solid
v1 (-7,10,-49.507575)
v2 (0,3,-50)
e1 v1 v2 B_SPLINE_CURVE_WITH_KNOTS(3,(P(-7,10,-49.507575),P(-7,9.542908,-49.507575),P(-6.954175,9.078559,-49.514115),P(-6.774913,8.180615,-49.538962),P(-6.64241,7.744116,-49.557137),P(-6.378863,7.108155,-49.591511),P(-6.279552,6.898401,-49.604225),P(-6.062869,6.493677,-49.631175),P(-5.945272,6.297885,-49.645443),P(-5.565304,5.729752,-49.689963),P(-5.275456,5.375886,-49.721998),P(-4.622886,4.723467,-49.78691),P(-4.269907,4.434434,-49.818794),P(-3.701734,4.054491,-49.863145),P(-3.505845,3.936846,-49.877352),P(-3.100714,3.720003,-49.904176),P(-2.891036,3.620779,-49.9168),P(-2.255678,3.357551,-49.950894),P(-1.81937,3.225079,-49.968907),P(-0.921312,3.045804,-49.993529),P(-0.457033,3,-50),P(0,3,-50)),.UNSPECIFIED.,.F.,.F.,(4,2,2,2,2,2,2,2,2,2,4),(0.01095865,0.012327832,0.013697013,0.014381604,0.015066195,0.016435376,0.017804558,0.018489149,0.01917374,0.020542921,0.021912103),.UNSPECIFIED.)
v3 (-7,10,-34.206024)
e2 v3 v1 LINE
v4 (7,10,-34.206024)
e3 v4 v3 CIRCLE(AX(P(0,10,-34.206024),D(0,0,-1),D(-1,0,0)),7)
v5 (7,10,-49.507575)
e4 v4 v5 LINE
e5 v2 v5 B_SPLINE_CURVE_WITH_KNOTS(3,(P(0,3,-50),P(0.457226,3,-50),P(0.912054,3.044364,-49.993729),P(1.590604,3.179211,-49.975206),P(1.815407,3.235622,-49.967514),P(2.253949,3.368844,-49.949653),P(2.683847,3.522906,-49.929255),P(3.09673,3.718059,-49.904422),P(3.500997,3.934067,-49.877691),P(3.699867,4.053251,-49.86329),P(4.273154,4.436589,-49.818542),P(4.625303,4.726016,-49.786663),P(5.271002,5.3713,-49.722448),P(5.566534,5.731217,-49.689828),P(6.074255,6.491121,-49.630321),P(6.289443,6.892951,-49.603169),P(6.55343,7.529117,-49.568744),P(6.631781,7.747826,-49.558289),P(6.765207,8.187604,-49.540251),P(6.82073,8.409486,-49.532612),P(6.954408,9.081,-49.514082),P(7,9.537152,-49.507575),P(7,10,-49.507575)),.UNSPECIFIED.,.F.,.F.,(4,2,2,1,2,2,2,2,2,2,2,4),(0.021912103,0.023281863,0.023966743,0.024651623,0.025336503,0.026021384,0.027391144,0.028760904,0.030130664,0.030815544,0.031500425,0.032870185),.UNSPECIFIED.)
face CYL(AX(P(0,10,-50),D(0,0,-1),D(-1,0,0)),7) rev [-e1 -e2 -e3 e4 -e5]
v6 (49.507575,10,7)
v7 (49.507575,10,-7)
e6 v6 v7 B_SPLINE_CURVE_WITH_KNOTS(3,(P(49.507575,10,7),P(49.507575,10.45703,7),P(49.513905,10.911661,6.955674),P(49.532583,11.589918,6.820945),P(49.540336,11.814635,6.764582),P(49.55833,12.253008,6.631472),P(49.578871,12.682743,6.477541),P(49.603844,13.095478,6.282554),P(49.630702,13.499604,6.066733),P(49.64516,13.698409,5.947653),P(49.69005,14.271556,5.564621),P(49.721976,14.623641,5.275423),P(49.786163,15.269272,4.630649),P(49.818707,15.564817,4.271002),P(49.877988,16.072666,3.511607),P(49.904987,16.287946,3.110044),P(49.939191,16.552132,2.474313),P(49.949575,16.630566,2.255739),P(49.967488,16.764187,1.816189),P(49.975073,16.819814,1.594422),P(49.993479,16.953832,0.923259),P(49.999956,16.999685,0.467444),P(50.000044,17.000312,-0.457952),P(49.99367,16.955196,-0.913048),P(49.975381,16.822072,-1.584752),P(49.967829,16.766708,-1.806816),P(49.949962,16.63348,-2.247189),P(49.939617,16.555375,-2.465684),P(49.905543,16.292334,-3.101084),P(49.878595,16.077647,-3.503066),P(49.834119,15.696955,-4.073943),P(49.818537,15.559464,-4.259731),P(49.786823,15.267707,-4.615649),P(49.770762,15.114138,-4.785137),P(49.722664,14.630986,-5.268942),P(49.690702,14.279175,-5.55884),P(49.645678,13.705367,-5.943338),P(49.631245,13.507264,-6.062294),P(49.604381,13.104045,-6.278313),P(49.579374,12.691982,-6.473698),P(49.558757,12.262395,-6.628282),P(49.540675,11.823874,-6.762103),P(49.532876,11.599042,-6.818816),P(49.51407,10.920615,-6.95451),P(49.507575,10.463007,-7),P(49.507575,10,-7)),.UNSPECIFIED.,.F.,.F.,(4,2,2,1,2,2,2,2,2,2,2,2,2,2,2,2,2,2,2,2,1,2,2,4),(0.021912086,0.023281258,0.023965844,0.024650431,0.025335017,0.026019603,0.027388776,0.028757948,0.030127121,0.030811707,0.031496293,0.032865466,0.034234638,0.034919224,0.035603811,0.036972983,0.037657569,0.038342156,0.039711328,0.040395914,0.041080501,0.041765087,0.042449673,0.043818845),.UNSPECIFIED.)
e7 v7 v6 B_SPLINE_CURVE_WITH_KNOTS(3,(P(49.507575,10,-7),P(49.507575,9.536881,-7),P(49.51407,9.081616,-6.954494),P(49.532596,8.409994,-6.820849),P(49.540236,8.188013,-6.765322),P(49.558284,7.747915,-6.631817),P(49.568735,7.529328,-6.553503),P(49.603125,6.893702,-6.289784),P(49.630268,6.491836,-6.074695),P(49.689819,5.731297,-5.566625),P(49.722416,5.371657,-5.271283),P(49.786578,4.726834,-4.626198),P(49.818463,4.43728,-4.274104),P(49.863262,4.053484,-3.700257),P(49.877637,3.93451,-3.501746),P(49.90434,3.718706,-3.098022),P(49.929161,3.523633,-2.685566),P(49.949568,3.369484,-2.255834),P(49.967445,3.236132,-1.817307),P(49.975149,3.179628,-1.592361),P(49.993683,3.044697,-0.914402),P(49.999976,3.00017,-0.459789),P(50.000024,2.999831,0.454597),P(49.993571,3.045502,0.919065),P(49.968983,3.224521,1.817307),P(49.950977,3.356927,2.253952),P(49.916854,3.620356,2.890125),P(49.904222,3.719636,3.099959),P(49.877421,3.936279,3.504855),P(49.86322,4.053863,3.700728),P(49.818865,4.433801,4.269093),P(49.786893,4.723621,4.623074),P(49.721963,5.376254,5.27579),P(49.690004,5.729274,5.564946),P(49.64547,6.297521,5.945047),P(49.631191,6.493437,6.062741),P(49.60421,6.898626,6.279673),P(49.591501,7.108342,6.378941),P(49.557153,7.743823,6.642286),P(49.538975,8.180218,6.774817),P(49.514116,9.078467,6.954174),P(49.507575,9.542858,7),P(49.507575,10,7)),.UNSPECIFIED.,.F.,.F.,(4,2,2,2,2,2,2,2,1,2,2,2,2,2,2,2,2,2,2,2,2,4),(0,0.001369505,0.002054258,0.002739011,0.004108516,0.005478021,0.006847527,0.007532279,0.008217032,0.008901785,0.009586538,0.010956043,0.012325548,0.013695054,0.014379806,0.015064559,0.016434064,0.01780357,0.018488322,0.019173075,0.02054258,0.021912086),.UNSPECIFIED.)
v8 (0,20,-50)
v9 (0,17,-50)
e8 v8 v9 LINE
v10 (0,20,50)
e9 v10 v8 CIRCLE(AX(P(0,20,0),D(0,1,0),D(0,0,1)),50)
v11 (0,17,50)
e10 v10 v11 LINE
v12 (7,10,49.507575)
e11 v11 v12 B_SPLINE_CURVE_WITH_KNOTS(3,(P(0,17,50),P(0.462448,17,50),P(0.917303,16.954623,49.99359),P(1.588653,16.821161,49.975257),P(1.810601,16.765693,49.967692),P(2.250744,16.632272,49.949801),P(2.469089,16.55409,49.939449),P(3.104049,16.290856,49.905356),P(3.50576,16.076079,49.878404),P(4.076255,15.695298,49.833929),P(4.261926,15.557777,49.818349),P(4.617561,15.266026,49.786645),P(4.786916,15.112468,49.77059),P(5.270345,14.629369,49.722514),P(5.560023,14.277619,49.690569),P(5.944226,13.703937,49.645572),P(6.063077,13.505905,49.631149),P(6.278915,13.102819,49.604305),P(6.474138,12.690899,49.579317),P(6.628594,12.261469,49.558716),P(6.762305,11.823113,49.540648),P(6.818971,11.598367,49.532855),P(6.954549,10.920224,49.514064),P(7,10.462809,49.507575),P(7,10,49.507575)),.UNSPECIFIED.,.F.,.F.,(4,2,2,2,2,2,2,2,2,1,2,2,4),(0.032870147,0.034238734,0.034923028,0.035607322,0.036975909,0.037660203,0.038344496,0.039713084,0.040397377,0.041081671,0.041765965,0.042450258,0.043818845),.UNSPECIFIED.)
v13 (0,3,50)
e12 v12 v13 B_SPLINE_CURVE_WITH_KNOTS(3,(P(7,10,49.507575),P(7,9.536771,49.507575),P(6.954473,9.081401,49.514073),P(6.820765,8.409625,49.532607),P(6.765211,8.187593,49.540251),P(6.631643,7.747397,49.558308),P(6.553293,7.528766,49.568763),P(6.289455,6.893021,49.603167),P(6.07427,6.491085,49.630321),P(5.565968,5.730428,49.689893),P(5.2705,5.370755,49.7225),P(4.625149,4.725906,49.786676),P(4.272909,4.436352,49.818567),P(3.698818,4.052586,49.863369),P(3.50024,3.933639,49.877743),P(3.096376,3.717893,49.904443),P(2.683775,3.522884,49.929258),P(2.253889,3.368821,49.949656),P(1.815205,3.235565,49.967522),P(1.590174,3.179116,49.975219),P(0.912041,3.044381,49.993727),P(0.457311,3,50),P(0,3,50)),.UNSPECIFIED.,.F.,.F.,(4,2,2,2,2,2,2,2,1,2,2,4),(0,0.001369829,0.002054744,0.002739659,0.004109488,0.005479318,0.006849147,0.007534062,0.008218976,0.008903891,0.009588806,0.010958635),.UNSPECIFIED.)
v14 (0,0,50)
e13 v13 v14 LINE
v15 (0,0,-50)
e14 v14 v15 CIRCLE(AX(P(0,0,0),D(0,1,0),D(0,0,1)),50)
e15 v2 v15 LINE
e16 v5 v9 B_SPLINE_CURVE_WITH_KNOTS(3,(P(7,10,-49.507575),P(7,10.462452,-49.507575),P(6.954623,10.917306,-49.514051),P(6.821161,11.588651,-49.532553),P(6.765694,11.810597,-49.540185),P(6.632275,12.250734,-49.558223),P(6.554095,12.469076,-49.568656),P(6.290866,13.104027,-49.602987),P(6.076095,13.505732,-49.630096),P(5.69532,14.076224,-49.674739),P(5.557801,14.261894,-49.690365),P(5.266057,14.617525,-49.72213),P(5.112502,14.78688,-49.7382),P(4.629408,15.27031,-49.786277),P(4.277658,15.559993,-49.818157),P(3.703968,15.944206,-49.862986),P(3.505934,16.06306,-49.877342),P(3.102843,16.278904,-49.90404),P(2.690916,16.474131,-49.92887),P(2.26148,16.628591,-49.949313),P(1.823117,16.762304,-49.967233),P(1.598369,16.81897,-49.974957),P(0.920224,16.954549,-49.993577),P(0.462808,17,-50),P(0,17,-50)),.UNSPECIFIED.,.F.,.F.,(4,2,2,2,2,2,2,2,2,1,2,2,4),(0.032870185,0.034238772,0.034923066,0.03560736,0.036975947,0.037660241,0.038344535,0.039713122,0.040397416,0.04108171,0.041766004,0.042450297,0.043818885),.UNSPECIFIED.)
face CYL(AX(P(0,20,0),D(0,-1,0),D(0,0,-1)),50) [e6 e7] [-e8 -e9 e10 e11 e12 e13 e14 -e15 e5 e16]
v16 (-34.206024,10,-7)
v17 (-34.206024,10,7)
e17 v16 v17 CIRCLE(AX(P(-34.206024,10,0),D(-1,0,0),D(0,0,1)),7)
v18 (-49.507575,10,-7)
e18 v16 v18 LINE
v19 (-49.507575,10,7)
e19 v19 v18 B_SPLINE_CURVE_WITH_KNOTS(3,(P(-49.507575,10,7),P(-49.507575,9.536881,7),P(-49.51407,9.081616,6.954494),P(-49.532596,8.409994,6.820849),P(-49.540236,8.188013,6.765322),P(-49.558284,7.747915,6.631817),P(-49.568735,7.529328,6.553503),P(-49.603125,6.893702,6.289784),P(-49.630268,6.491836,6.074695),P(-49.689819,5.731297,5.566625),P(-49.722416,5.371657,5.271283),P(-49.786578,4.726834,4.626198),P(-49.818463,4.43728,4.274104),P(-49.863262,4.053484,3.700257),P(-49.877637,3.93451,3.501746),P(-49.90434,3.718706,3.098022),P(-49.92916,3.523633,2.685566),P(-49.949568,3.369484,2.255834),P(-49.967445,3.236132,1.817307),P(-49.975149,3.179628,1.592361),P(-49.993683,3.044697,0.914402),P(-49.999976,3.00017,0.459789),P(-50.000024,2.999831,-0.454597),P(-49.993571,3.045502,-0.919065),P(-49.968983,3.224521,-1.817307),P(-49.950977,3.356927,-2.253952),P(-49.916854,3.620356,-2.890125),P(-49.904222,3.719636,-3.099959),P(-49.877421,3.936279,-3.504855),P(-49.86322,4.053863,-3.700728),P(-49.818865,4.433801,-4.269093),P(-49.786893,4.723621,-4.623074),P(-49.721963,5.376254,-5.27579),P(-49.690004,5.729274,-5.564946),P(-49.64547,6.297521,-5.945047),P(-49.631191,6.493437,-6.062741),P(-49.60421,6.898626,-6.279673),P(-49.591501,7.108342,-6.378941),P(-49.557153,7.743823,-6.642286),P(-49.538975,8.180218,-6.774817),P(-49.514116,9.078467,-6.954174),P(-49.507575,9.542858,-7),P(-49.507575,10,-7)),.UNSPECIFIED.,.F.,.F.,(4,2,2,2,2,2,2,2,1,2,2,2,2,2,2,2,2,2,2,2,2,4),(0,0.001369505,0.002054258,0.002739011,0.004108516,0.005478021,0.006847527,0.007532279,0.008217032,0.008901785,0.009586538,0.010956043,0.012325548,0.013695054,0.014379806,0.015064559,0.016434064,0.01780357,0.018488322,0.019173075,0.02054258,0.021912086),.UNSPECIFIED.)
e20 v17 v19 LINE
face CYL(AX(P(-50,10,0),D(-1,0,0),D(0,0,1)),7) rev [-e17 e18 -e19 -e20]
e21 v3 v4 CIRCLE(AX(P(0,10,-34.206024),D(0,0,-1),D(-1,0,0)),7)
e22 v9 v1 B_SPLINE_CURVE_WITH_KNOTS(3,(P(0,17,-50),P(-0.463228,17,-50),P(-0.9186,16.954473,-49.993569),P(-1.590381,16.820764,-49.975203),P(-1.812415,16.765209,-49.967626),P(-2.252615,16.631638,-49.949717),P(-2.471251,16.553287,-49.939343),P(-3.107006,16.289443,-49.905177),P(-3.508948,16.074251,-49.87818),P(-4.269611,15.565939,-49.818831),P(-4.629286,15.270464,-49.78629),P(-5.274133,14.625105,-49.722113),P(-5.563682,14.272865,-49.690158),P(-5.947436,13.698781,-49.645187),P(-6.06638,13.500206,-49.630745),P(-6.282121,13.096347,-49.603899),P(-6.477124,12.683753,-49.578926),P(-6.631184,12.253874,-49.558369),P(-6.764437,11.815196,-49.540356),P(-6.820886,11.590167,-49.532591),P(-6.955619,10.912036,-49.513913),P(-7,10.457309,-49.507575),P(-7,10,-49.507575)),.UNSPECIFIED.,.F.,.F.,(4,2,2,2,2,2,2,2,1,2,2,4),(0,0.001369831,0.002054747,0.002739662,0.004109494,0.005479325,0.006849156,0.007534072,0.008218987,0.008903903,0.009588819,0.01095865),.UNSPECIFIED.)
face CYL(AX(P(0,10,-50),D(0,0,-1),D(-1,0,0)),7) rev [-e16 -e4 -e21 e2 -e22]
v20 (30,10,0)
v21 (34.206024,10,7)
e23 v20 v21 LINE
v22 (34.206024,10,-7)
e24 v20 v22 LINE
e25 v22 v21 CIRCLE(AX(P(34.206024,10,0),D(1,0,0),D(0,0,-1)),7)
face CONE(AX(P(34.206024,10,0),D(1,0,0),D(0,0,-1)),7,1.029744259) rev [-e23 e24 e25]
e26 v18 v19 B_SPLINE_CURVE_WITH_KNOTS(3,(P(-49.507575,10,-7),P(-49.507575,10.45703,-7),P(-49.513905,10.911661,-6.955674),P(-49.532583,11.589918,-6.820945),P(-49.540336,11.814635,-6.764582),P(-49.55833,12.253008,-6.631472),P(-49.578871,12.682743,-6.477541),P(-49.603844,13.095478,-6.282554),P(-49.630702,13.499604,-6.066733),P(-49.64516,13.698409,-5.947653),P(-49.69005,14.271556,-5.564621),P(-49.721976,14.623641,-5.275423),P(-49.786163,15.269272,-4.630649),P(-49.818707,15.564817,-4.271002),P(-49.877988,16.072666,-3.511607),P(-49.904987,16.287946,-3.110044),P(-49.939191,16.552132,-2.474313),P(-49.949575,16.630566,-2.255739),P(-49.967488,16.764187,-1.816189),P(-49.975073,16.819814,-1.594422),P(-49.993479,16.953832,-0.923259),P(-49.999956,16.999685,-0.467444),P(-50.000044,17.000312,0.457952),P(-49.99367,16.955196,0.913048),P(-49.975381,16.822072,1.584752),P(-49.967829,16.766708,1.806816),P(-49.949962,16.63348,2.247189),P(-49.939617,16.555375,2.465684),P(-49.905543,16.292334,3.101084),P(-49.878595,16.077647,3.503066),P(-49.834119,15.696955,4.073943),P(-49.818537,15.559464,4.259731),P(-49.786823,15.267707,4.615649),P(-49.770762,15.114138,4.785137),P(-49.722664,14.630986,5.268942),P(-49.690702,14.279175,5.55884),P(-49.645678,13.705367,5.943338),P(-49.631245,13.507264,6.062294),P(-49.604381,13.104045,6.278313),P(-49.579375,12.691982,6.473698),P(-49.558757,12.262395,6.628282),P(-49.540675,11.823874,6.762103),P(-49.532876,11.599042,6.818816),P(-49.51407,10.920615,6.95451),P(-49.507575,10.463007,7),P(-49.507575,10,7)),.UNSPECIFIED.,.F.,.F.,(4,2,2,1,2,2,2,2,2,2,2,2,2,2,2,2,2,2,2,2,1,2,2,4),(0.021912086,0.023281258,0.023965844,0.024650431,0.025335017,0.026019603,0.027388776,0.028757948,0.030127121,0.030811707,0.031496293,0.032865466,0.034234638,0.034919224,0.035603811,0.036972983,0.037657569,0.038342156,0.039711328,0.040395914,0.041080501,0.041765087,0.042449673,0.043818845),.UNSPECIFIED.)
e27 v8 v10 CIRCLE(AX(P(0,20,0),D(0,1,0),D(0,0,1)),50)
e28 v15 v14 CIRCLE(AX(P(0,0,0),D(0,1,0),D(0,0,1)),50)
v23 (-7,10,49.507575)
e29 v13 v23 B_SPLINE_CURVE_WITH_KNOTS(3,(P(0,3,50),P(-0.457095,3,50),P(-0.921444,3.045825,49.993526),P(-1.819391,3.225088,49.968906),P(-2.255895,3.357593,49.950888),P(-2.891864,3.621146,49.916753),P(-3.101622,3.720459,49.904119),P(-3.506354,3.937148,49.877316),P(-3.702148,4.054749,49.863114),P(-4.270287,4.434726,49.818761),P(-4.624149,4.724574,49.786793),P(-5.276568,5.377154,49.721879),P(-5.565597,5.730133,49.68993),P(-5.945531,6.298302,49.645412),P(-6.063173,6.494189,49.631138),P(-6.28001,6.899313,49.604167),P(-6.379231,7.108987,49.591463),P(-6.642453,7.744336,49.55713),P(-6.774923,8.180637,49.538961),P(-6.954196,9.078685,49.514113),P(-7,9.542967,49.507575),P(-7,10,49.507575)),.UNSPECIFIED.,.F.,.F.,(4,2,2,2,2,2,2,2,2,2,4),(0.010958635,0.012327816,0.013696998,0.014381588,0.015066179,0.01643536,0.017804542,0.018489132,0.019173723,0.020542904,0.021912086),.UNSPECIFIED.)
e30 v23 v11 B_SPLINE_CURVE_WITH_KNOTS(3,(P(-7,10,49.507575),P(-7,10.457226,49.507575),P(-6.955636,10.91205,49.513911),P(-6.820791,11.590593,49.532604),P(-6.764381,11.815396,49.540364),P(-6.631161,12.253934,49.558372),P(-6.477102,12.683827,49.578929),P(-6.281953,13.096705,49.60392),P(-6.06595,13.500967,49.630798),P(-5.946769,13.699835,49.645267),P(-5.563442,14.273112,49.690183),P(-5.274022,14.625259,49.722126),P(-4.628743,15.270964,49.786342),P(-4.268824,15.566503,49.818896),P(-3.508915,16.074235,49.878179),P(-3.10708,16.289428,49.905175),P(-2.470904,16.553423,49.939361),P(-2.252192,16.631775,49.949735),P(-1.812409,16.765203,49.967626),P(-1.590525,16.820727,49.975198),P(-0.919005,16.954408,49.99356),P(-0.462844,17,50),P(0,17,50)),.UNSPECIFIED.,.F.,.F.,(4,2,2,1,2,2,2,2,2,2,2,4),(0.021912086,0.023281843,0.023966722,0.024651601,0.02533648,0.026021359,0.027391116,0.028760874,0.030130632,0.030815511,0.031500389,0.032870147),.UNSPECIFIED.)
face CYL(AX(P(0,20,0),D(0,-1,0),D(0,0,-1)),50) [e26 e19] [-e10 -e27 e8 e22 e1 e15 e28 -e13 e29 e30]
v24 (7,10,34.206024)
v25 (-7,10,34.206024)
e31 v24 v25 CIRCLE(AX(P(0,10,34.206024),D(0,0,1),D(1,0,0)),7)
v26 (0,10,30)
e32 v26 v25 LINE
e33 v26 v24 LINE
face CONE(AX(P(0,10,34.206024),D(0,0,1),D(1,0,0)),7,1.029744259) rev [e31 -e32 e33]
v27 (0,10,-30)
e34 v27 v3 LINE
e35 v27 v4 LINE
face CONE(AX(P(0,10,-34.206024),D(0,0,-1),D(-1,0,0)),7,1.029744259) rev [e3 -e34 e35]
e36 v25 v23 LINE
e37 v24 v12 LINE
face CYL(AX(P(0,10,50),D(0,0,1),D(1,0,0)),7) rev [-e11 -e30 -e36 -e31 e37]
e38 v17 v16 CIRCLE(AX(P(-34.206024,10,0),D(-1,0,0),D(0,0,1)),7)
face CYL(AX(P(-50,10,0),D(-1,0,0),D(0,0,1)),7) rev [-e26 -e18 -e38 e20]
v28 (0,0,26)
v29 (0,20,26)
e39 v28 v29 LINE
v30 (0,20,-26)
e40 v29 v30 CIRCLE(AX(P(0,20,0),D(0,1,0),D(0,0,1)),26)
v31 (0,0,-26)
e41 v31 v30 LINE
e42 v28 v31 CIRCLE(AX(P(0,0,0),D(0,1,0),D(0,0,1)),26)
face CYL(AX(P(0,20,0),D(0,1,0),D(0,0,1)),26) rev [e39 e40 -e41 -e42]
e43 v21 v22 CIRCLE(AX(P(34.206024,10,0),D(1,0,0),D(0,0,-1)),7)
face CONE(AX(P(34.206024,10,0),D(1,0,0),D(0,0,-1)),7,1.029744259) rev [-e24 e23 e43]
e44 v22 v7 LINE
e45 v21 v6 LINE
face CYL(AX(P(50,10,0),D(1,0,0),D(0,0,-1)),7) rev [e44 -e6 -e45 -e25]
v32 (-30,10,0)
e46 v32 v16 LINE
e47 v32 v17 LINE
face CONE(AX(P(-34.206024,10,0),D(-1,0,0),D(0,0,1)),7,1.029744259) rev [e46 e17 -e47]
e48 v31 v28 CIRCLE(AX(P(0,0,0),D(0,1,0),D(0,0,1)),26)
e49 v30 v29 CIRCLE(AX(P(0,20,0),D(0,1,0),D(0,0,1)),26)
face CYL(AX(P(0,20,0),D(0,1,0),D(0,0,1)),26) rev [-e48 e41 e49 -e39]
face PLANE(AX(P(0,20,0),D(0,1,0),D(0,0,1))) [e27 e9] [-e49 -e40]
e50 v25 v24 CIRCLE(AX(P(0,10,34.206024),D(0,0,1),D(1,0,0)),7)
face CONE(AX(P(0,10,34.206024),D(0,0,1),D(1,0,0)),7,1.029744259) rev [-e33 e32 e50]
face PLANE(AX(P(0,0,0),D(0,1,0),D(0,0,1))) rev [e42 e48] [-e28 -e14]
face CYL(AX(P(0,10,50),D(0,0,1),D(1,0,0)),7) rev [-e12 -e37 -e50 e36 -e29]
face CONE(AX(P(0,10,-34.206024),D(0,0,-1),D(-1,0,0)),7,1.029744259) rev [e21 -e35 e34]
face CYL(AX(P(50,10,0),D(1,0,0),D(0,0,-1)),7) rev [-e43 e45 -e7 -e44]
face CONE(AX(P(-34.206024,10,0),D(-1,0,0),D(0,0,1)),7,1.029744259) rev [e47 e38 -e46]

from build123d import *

# Parameters (mm, degrees)
SKETCH1_R                  = 50
BOSS_EXTRUDE1_DEPTH        = 20
M56X4_0_TAPPED_HOLE1_D     = 52
M56X4_0_TAPPED_HOLE1_DEPTH = 124
M56X4_0_TAPPED_HOLE1_TIP   = 15.622376095
CIRPATTERN1_COUNT          = 4


with BuildPart() as part:
    # Sketch1 → Boss-Extrude1 (new body)
    with BuildSketch(Plane(origin=(0, 0, 0), x_dir=(1, 0, 0), z_dir=(0, 1, 0))):
        with Locations(Location((0, 0, 0), (0, 0, 270))):
            Circle(SKETCH1_R)
    extrude(amount=BOSS_EXTRUDE1_DEPTH)

    # M56x4.0 Tapped Hole1
    with Locations(Plane(origin=(0, 20, 0), x_dir=(1, 0, 0), z_dir=(0, 1, 0))):
        with Locations((0, 0)):
            Hole(M56X4_0_TAPPED_HOLE1_D / 2, depth=M56X4_0_TAPPED_HOLE1_DEPTH)
            with Locations((0, 0, -(M56X4_0_TAPPED_HOLE1_DEPTH + M56X4_0_TAPPED_HOLE1_TIP / 2))):  # 118° drill point
                Cone(0, M56X4_0_TAPPED_HOLE1_D / 2, M56X4_0_TAPPED_HOLE1_TIP, mode=Mode.SUBTRACT)

    # Sketch5 → Ø14.0 (14) Diameter Hole1 (revolve, cut)
    with BuildSketch(Plane(origin=(0, 10, 50), x_dir=(0, -1, 0), z_dir=(1, 0, 0))):
        Polygon((0, 0), (0, 20), (7, 15.793975667), (7, 0), align=None)
    f_14_0_14_diameter_hole1 = revolve(axis=Axis((0, 10, 56.35), (0, 0, -1)), mode=Mode.SUBTRACT)

    # CirPattern1: Ø14.0 (14) Diameter Hole1 ×4 about axis
    cirpattern1_axis = Axis((0, 20, 0), (0, 1, 0))
    for i in range(1, CIRPATTERN1_COUNT):
        add(f_14_0_14_diameter_hole1.rotate(cirpattern1_axis, i * 360 / CIRPATTERN1_COUNT), mode=Mode.SUBTRACT)


solid = part.part
